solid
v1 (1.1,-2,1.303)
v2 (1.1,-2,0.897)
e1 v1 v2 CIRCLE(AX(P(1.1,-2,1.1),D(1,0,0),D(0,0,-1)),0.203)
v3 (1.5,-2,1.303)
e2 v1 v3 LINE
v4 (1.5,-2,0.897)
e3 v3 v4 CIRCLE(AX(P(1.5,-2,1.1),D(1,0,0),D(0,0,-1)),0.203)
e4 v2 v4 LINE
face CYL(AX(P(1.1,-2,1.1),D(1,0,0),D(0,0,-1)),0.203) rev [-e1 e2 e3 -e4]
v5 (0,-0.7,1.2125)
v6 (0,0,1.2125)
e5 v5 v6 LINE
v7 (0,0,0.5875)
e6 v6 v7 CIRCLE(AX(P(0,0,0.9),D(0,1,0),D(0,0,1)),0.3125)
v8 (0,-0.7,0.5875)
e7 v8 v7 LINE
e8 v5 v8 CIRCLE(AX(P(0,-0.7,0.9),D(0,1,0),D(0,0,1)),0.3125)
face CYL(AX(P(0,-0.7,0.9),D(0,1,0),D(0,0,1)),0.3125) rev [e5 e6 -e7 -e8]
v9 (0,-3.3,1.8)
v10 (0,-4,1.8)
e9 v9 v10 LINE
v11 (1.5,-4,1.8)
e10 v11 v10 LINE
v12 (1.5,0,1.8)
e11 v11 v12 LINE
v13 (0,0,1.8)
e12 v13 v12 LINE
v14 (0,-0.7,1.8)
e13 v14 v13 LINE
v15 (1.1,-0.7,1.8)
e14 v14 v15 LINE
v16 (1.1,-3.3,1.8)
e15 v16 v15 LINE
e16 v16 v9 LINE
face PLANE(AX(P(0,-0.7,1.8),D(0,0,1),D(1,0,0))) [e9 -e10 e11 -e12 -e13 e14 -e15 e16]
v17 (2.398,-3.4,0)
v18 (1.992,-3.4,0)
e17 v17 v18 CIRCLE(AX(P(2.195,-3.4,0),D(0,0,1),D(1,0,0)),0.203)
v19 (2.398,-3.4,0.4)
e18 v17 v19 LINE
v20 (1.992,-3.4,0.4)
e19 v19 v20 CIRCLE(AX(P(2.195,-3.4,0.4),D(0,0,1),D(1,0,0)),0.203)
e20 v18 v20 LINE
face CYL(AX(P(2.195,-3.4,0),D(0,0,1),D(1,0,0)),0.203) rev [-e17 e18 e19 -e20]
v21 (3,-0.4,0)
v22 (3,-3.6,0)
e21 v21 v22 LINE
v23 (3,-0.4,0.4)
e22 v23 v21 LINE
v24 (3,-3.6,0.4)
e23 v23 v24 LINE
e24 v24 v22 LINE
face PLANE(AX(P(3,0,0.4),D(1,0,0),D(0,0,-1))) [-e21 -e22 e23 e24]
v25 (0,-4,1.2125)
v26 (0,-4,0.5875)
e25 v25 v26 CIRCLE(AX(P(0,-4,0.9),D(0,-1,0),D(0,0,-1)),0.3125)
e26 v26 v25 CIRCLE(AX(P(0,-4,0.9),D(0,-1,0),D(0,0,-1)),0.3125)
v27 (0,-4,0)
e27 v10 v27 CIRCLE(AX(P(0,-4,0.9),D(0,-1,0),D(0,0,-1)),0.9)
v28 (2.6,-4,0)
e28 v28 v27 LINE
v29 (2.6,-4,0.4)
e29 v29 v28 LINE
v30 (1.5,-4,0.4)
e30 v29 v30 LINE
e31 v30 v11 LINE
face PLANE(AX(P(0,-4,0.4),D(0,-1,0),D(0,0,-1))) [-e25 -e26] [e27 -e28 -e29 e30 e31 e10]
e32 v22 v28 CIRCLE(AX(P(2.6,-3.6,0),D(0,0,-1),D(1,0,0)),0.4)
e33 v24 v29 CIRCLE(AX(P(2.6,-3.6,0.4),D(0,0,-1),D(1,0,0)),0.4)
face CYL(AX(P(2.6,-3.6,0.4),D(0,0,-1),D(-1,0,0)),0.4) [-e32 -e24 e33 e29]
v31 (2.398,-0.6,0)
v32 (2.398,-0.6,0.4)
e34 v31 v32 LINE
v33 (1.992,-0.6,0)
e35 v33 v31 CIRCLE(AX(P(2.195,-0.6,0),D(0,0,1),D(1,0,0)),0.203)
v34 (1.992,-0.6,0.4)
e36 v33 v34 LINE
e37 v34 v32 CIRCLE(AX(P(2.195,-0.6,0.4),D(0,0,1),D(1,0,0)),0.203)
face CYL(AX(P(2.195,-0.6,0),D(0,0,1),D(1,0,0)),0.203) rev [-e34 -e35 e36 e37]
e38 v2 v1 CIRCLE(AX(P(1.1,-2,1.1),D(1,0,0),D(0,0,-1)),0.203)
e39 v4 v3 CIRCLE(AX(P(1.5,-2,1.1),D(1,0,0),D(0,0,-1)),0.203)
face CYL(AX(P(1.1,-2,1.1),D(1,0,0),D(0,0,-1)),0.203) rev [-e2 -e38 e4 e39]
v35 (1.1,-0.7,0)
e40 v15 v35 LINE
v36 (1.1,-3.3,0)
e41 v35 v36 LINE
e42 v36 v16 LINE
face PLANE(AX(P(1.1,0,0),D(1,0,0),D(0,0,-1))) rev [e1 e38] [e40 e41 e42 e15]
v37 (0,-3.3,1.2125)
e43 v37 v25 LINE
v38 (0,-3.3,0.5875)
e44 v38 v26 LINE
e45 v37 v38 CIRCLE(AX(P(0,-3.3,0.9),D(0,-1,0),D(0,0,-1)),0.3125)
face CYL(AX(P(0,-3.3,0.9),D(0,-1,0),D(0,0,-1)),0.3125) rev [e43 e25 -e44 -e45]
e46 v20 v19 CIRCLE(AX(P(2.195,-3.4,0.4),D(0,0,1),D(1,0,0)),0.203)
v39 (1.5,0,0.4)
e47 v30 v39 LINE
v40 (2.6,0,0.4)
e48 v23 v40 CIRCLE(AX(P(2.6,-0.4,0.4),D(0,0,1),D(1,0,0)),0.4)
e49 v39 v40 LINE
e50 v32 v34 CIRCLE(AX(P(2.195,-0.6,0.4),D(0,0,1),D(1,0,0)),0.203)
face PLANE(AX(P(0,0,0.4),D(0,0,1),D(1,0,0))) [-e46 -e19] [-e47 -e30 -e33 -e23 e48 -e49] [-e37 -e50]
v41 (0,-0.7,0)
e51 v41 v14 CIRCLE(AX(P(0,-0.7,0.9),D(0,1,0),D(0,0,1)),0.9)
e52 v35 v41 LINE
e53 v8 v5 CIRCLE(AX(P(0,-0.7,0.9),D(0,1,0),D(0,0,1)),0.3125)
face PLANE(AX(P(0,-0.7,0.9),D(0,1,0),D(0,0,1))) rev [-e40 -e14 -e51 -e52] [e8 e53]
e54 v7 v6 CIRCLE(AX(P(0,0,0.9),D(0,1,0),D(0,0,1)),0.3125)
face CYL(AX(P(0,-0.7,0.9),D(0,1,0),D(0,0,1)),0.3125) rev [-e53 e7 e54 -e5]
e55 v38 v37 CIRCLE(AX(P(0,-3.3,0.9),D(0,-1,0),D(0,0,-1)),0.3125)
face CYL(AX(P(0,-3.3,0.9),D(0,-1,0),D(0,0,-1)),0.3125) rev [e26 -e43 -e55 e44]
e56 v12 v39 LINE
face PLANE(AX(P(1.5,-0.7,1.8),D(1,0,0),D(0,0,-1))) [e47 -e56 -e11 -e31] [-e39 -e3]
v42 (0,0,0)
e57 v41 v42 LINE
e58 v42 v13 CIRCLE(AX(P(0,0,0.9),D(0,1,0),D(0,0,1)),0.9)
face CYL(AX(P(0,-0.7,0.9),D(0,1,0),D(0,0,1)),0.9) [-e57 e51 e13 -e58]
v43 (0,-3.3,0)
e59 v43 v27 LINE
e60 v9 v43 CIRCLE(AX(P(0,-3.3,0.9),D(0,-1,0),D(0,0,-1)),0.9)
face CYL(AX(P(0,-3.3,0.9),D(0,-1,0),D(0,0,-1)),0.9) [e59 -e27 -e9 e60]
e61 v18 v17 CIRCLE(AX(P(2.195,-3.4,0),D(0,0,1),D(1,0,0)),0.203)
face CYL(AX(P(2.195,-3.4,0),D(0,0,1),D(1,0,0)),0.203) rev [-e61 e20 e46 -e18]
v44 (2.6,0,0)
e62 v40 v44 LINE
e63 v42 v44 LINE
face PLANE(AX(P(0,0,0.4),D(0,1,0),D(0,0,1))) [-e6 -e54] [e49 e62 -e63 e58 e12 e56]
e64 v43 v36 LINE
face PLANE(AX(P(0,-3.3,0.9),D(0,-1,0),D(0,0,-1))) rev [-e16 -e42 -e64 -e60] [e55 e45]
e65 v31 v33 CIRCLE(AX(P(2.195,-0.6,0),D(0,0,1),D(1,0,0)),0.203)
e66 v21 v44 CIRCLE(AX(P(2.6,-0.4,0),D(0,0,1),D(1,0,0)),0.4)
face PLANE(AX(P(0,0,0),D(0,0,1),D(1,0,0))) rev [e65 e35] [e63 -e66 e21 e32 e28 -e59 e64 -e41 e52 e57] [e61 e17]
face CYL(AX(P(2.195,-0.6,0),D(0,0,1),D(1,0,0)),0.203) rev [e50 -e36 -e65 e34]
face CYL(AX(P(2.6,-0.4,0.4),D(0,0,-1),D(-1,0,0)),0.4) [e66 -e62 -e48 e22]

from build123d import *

# Parameters (mm, degrees)
C_FRAME_BASE_DEPTH       = 0.4
CLEVIS_GAP_SKETCH_W      = 0.4
CLEVIS_GAP_SKETCH_H      = 4
CLEVIS_GAP_CUT_DEPTH     = 1.5
CLEVIS_ARM_1_DEPTH       = 0.7
CLEVIS_START             = -0.7
CLEVIS_ARM_2_DEPTH       = 0.7
MOUNTING_FLANGE_SKETCH_W = 1.8
MOUNTING_FLANGE_SKETCH_H = 2.6
MOUNTING_FLANGE_DEPTH    = 0.4
BACK_WALL_HOLE_SKETCH_R  = 0.203
BACK_WALL_HOLE_DEPTH     = 0.4
FLANGE_HOLES_SKETCH_R    = 0.203
FLANGE_HOLES_2X_DEPTH    = 0.4
ARM_1_PIN_HOLE_SKETCH_R  = 0.3125
ARM_1_PIN_HOLE_DEPTH     = 0.7
ARM_START                = -0.7
ARM_2_PIN_HOLE_SKETCH_R  = 0.3125
ARM_2_PIN_HOLE_DEPTH     = 0.7


with BuildPart() as part:
    # C-Frame Profile Sketch → C-Frame Base (new body)
    with BuildSketch(Plane.XY):
        with BuildLine():
            ThreePointArc((3, -3.6), (2.882842712, -3.882842712), (2.6, -4))
            Line((2.6, -4), (0, -4))
            Line((0, -4), (0, 0))
            Line((0, 0), (2.6, 0))
            ThreePointArc((2.6, 0), (2.882842712, -0.117157288), (3, -0.4))
            Line((3, -0.4), (3, -3.6))
        make_face()
    extrude(amount=C_FRAME_BASE_DEPTH)

    # Clevis Gap Sketch → Clevis Gap Cut (cut)
    with BuildSketch(Plane.ZY):
        with Locations((0.2, -2)):
            Rectangle(CLEVIS_GAP_SKETCH_W, CLEVIS_GAP_SKETCH_H)
    extrude(amount=-CLEVIS_GAP_CUT_DEPTH, mode=Mode.SUBTRACT)

    # Clevis Arm 1 Sketch → Clevis Arm 1 (add)
    with BuildSketch(Plane(origin=(0, 0, 0), x_dir=(1, 0, 0), z_dir=(0, 1, 0))):
        with BuildLine():
            Line((1.5, 0), (0, 0))
            ThreePointArc((0, 0), (-0.9, -0.9), (0, -1.8))
            Line((0, -1.8), (1.5, -1.8))
            Line((1.5, -1.8), (1.5, 0))
        make_face()
    extrude(amount=-CLEVIS_ARM_1_DEPTH)

    # Clevis Arm 2 Sketch → Clevis Arm 2 (add)
    with BuildSketch(Plane.XZ.offset(4).offset(CLEVIS_START)):
        with BuildLine():
            Line((1.5, 0), (0, 0))
            ThreePointArc((0, 0), (-0.9, 0.9), (0, 1.8))
            Line((0, 1.8), (1.5, 1.8))
            Line((1.5, 1.8), (1.5, 0))
        make_face()
    extrude(amount=CLEVIS_ARM_2_DEPTH)

    # Mounting Flange Sketch → Mounting Flange (add)
    with BuildSketch(Plane.ZY.offset(-1.5)):
        with Locations((0.9, -2)):
            Rectangle(MOUNTING_FLANGE_SKETCH_W, MOUNTING_FLANGE_SKETCH_H)
    extrude(amount=MOUNTING_FLANGE_DEPTH)

    # Back Wall Hole Sketch → Back Wall Hole (cut)
    with BuildSketch(Plane(origin=(1.5, 0, 0), x_dir=(0, 0, -1), z_dir=(1, 0, 0))):
        with Locations((-1.1, -2)):
            Circle(BACK_WALL_HOLE_SKETCH_R)
    extrude(amount=-BACK_WALL_HOLE_DEPTH, mode=Mode.SUBTRACT)

    # Flange Holes Sketch → Flange Holes 2x (cut)
    with BuildSketch(Plane.XY.offset(0.4)):
        with Locations((2.195, -0.6)):
            Circle(FLANGE_HOLES_SKETCH_R)
        with Locations((2.195, -3.4)):
            Circle(FLANGE_HOLES_SKETCH_R)
    extrude(amount=-FLANGE_HOLES_2X_DEPTH, mode=Mode.SUBTRACT)

    # Arm 1 Pin Hole Sketch → Arm 1 Pin Hole (cut)
    with BuildSketch(Plane(origin=(0, 0, 0), x_dir=(1, 0, 0), z_dir=(0, 1, 0))):
        with Locations(Location((0, -0.9, 0), (0, 0, 270))):
            Circle(ARM_1_PIN_HOLE_SKETCH_R)
    extrude(amount=-ARM_1_PIN_HOLE_DEPTH, mode=Mode.SUBTRACT)

    # Arm 2 Pin Hole Sketch → Arm 2 Pin Hole (cut)
    with BuildSketch(Plane.XZ.offset(4).offset(ARM_START)):
        with Locations(Location((0, 0.9, 0), (0, 0, 90))):
            Circle(ARM_2_PIN_HOLE_SKETCH_R)
    extrude(amount=ARM_2_PIN_HOLE_DEPTH, mode=Mode.SUBTRACT)


solid = part.part
